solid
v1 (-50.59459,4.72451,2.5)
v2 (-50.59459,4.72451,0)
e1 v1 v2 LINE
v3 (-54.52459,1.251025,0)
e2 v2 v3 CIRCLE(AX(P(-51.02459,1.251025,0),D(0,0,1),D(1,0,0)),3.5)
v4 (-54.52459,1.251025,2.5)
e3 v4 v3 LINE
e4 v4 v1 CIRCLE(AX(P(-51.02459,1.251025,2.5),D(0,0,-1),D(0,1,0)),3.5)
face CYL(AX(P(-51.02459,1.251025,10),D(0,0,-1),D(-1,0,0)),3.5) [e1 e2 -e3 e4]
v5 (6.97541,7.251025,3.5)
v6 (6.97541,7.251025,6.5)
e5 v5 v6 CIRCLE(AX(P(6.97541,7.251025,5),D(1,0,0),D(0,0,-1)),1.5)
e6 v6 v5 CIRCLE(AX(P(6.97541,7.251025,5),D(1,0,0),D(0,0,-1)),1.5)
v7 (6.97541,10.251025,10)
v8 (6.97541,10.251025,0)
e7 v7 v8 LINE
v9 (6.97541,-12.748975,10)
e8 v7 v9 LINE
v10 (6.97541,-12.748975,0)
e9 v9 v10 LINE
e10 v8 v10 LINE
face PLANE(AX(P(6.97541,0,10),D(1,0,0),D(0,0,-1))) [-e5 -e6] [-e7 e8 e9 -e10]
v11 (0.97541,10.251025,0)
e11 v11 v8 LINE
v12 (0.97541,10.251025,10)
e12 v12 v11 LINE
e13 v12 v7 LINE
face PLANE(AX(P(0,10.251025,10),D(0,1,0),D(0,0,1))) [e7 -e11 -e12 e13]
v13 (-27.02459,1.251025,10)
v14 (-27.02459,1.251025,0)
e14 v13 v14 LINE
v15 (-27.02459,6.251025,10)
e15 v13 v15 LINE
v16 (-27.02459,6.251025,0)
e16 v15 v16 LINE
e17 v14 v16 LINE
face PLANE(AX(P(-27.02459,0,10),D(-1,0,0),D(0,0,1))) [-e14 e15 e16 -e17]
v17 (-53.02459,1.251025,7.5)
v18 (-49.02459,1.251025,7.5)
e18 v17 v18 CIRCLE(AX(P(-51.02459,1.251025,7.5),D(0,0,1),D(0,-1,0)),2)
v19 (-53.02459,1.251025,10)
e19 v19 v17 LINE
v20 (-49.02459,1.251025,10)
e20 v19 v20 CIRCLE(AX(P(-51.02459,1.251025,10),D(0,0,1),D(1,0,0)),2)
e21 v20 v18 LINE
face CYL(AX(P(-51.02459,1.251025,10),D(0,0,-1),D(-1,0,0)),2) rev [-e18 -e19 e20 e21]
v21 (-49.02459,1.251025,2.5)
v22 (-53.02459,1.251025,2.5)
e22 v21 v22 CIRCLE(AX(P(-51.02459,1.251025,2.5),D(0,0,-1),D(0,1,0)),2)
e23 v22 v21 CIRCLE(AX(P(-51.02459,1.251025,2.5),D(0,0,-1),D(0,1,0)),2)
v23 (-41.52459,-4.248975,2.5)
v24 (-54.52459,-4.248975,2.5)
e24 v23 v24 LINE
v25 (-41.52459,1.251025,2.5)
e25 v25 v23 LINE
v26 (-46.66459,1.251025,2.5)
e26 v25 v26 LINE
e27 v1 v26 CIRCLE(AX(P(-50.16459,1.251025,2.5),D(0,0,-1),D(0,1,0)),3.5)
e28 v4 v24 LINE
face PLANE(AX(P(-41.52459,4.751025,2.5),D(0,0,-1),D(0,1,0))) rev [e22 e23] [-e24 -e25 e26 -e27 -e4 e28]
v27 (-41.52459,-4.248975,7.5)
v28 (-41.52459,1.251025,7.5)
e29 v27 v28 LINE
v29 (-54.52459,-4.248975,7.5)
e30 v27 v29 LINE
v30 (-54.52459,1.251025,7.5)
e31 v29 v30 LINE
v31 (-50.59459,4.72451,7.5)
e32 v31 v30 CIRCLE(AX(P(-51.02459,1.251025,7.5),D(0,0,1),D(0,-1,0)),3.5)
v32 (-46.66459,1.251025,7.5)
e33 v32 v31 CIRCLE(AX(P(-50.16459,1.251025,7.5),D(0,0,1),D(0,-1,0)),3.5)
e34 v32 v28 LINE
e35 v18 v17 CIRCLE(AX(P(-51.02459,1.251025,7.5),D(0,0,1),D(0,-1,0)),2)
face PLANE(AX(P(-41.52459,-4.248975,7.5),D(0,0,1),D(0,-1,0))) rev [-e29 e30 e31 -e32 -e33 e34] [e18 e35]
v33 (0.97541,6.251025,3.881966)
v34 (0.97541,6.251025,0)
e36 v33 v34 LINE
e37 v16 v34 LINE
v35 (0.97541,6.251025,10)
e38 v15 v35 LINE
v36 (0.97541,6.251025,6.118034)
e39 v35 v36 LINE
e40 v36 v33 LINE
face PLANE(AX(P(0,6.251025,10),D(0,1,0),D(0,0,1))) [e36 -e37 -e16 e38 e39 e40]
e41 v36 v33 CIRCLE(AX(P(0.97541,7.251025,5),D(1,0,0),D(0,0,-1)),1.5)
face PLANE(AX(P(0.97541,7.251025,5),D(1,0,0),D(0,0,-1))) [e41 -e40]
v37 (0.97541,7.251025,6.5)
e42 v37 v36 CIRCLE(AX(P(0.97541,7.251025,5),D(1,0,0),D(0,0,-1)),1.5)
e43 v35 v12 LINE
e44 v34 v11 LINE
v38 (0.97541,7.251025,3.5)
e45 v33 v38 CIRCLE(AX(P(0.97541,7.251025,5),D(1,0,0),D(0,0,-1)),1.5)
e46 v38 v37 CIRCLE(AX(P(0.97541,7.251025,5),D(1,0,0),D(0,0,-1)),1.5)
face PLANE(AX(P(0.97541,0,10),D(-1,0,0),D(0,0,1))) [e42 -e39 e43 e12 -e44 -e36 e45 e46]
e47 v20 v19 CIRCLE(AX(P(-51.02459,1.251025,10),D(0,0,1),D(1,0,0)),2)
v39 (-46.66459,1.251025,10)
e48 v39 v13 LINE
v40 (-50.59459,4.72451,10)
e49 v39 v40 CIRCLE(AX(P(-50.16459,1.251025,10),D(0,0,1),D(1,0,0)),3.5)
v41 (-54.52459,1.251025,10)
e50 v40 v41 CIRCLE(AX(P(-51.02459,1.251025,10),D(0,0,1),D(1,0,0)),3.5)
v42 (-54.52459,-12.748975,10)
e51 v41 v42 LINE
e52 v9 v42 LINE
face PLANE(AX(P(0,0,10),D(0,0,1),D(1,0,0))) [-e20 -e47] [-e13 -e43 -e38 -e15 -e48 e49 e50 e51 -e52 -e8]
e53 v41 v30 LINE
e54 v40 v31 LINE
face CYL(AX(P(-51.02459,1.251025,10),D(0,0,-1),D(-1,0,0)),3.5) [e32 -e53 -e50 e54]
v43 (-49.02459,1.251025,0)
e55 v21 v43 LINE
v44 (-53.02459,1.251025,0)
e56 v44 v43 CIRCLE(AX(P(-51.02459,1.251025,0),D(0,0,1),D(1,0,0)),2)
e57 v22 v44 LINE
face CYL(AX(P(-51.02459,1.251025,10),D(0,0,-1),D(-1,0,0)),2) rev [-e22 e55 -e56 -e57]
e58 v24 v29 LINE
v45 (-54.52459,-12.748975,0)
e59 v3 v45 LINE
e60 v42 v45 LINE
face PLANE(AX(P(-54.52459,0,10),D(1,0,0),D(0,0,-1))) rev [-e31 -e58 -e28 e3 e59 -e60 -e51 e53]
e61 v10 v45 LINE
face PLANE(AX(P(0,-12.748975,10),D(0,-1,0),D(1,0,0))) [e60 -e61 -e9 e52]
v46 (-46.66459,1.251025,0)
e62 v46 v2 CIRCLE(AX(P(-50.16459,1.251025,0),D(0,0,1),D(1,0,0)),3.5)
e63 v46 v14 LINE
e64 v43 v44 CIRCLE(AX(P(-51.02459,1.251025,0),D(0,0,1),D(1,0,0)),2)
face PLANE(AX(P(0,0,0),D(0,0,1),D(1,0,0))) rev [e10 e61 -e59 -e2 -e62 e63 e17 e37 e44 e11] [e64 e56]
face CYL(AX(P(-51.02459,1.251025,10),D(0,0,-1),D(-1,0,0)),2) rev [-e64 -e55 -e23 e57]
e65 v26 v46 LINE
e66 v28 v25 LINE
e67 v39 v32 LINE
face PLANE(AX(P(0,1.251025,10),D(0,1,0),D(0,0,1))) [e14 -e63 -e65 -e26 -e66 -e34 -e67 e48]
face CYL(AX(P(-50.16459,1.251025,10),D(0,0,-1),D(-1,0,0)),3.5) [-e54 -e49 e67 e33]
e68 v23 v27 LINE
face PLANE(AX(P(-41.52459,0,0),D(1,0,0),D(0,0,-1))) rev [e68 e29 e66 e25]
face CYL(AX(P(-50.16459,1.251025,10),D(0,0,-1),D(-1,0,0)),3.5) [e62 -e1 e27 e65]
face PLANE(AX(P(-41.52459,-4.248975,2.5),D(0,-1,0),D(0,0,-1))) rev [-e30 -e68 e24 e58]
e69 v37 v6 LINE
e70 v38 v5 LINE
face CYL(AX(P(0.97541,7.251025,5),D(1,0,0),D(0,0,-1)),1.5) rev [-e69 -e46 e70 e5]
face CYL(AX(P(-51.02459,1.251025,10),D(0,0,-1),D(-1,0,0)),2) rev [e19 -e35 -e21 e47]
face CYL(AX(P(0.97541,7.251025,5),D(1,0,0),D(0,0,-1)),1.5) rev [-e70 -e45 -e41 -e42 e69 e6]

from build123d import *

# Parameters (mm, degrees)
SKETCH_1_R          = 2
EXTRUDE_1_DEPTH     = 10
SKETCH_2_R          = 1.5
CUT_EXTRUDE_1_DEPTH = 6
SKETCH_3_W          = 5
SKETCH_3_H          = 9
CUT_EXTRUDE_2_DEPTH = 13


with BuildPart() as part:
    # 草图1 → 凸台-拉伸1 (new body)
    with BuildSketch(Plane.XY):
        with BuildLine():
            Line((-46.664590164, 1.25102459), (-27.024590164, 1.25102459))
            Line((-27.024590164, 1.25102459), (-27.024590164, 6.25102459))
            Line((-27.024590164, 6.25102459), (0.975409836, 6.25102459))
            Line((0.975409836, 6.25102459), (0.975409836, 10.25102459))
            Line((0.975409836, 10.25102459), (6.975409836, 10.25102459))
            Line((6.975409836, 10.25102459), (6.975409836, -12.74897541))
            Line((6.975409836, -12.74897541), (-54.524590164, -12.74897541))
            Line((-54.524590164, -12.74897541), (-54.524590164, 1.25102459))
            ThreePointArc((-54.524590164, 1.25102459), (-53.342455561, 3.873523399), (-50.594590164, 4.724509872))
            ThreePointArc((-50.594590164, 4.724509872), (-47.846724767, 3.873523399), (-46.664590164, 1.25102459))
        make_face()
        with Locations((-51.024590164, 1.25102459)):
            Circle(SKETCH_1_R, mode=Mode.SUBTRACT)
    extrude(amount=EXTRUDE_1_DEPTH)

    # 草图2 → 切除-拉伸1 (cut)
    with BuildSketch(Plane(origin=(6.975409836, 0, 0), x_dir=(0, 0, -1), z_dir=(1, 0, 0))):
        with Locations((-5, 7.25102459)):
            Circle(SKETCH_2_R)
    extrude(amount=-CUT_EXTRUDE_1_DEPTH, mode=Mode.SUBTRACT)

    # 草图3 → 切除-拉伸2 (cut)
    with BuildSketch(Plane.ZY.offset(54.524590164)):
        with Locations((5, 0.25102459)):
            Rectangle(SKETCH_3_W, SKETCH_3_H)
    extrude(amount=-CUT_EXTRUDE_2_DEPTH, mode=Mode.SUBTRACT)


solid = part.part
